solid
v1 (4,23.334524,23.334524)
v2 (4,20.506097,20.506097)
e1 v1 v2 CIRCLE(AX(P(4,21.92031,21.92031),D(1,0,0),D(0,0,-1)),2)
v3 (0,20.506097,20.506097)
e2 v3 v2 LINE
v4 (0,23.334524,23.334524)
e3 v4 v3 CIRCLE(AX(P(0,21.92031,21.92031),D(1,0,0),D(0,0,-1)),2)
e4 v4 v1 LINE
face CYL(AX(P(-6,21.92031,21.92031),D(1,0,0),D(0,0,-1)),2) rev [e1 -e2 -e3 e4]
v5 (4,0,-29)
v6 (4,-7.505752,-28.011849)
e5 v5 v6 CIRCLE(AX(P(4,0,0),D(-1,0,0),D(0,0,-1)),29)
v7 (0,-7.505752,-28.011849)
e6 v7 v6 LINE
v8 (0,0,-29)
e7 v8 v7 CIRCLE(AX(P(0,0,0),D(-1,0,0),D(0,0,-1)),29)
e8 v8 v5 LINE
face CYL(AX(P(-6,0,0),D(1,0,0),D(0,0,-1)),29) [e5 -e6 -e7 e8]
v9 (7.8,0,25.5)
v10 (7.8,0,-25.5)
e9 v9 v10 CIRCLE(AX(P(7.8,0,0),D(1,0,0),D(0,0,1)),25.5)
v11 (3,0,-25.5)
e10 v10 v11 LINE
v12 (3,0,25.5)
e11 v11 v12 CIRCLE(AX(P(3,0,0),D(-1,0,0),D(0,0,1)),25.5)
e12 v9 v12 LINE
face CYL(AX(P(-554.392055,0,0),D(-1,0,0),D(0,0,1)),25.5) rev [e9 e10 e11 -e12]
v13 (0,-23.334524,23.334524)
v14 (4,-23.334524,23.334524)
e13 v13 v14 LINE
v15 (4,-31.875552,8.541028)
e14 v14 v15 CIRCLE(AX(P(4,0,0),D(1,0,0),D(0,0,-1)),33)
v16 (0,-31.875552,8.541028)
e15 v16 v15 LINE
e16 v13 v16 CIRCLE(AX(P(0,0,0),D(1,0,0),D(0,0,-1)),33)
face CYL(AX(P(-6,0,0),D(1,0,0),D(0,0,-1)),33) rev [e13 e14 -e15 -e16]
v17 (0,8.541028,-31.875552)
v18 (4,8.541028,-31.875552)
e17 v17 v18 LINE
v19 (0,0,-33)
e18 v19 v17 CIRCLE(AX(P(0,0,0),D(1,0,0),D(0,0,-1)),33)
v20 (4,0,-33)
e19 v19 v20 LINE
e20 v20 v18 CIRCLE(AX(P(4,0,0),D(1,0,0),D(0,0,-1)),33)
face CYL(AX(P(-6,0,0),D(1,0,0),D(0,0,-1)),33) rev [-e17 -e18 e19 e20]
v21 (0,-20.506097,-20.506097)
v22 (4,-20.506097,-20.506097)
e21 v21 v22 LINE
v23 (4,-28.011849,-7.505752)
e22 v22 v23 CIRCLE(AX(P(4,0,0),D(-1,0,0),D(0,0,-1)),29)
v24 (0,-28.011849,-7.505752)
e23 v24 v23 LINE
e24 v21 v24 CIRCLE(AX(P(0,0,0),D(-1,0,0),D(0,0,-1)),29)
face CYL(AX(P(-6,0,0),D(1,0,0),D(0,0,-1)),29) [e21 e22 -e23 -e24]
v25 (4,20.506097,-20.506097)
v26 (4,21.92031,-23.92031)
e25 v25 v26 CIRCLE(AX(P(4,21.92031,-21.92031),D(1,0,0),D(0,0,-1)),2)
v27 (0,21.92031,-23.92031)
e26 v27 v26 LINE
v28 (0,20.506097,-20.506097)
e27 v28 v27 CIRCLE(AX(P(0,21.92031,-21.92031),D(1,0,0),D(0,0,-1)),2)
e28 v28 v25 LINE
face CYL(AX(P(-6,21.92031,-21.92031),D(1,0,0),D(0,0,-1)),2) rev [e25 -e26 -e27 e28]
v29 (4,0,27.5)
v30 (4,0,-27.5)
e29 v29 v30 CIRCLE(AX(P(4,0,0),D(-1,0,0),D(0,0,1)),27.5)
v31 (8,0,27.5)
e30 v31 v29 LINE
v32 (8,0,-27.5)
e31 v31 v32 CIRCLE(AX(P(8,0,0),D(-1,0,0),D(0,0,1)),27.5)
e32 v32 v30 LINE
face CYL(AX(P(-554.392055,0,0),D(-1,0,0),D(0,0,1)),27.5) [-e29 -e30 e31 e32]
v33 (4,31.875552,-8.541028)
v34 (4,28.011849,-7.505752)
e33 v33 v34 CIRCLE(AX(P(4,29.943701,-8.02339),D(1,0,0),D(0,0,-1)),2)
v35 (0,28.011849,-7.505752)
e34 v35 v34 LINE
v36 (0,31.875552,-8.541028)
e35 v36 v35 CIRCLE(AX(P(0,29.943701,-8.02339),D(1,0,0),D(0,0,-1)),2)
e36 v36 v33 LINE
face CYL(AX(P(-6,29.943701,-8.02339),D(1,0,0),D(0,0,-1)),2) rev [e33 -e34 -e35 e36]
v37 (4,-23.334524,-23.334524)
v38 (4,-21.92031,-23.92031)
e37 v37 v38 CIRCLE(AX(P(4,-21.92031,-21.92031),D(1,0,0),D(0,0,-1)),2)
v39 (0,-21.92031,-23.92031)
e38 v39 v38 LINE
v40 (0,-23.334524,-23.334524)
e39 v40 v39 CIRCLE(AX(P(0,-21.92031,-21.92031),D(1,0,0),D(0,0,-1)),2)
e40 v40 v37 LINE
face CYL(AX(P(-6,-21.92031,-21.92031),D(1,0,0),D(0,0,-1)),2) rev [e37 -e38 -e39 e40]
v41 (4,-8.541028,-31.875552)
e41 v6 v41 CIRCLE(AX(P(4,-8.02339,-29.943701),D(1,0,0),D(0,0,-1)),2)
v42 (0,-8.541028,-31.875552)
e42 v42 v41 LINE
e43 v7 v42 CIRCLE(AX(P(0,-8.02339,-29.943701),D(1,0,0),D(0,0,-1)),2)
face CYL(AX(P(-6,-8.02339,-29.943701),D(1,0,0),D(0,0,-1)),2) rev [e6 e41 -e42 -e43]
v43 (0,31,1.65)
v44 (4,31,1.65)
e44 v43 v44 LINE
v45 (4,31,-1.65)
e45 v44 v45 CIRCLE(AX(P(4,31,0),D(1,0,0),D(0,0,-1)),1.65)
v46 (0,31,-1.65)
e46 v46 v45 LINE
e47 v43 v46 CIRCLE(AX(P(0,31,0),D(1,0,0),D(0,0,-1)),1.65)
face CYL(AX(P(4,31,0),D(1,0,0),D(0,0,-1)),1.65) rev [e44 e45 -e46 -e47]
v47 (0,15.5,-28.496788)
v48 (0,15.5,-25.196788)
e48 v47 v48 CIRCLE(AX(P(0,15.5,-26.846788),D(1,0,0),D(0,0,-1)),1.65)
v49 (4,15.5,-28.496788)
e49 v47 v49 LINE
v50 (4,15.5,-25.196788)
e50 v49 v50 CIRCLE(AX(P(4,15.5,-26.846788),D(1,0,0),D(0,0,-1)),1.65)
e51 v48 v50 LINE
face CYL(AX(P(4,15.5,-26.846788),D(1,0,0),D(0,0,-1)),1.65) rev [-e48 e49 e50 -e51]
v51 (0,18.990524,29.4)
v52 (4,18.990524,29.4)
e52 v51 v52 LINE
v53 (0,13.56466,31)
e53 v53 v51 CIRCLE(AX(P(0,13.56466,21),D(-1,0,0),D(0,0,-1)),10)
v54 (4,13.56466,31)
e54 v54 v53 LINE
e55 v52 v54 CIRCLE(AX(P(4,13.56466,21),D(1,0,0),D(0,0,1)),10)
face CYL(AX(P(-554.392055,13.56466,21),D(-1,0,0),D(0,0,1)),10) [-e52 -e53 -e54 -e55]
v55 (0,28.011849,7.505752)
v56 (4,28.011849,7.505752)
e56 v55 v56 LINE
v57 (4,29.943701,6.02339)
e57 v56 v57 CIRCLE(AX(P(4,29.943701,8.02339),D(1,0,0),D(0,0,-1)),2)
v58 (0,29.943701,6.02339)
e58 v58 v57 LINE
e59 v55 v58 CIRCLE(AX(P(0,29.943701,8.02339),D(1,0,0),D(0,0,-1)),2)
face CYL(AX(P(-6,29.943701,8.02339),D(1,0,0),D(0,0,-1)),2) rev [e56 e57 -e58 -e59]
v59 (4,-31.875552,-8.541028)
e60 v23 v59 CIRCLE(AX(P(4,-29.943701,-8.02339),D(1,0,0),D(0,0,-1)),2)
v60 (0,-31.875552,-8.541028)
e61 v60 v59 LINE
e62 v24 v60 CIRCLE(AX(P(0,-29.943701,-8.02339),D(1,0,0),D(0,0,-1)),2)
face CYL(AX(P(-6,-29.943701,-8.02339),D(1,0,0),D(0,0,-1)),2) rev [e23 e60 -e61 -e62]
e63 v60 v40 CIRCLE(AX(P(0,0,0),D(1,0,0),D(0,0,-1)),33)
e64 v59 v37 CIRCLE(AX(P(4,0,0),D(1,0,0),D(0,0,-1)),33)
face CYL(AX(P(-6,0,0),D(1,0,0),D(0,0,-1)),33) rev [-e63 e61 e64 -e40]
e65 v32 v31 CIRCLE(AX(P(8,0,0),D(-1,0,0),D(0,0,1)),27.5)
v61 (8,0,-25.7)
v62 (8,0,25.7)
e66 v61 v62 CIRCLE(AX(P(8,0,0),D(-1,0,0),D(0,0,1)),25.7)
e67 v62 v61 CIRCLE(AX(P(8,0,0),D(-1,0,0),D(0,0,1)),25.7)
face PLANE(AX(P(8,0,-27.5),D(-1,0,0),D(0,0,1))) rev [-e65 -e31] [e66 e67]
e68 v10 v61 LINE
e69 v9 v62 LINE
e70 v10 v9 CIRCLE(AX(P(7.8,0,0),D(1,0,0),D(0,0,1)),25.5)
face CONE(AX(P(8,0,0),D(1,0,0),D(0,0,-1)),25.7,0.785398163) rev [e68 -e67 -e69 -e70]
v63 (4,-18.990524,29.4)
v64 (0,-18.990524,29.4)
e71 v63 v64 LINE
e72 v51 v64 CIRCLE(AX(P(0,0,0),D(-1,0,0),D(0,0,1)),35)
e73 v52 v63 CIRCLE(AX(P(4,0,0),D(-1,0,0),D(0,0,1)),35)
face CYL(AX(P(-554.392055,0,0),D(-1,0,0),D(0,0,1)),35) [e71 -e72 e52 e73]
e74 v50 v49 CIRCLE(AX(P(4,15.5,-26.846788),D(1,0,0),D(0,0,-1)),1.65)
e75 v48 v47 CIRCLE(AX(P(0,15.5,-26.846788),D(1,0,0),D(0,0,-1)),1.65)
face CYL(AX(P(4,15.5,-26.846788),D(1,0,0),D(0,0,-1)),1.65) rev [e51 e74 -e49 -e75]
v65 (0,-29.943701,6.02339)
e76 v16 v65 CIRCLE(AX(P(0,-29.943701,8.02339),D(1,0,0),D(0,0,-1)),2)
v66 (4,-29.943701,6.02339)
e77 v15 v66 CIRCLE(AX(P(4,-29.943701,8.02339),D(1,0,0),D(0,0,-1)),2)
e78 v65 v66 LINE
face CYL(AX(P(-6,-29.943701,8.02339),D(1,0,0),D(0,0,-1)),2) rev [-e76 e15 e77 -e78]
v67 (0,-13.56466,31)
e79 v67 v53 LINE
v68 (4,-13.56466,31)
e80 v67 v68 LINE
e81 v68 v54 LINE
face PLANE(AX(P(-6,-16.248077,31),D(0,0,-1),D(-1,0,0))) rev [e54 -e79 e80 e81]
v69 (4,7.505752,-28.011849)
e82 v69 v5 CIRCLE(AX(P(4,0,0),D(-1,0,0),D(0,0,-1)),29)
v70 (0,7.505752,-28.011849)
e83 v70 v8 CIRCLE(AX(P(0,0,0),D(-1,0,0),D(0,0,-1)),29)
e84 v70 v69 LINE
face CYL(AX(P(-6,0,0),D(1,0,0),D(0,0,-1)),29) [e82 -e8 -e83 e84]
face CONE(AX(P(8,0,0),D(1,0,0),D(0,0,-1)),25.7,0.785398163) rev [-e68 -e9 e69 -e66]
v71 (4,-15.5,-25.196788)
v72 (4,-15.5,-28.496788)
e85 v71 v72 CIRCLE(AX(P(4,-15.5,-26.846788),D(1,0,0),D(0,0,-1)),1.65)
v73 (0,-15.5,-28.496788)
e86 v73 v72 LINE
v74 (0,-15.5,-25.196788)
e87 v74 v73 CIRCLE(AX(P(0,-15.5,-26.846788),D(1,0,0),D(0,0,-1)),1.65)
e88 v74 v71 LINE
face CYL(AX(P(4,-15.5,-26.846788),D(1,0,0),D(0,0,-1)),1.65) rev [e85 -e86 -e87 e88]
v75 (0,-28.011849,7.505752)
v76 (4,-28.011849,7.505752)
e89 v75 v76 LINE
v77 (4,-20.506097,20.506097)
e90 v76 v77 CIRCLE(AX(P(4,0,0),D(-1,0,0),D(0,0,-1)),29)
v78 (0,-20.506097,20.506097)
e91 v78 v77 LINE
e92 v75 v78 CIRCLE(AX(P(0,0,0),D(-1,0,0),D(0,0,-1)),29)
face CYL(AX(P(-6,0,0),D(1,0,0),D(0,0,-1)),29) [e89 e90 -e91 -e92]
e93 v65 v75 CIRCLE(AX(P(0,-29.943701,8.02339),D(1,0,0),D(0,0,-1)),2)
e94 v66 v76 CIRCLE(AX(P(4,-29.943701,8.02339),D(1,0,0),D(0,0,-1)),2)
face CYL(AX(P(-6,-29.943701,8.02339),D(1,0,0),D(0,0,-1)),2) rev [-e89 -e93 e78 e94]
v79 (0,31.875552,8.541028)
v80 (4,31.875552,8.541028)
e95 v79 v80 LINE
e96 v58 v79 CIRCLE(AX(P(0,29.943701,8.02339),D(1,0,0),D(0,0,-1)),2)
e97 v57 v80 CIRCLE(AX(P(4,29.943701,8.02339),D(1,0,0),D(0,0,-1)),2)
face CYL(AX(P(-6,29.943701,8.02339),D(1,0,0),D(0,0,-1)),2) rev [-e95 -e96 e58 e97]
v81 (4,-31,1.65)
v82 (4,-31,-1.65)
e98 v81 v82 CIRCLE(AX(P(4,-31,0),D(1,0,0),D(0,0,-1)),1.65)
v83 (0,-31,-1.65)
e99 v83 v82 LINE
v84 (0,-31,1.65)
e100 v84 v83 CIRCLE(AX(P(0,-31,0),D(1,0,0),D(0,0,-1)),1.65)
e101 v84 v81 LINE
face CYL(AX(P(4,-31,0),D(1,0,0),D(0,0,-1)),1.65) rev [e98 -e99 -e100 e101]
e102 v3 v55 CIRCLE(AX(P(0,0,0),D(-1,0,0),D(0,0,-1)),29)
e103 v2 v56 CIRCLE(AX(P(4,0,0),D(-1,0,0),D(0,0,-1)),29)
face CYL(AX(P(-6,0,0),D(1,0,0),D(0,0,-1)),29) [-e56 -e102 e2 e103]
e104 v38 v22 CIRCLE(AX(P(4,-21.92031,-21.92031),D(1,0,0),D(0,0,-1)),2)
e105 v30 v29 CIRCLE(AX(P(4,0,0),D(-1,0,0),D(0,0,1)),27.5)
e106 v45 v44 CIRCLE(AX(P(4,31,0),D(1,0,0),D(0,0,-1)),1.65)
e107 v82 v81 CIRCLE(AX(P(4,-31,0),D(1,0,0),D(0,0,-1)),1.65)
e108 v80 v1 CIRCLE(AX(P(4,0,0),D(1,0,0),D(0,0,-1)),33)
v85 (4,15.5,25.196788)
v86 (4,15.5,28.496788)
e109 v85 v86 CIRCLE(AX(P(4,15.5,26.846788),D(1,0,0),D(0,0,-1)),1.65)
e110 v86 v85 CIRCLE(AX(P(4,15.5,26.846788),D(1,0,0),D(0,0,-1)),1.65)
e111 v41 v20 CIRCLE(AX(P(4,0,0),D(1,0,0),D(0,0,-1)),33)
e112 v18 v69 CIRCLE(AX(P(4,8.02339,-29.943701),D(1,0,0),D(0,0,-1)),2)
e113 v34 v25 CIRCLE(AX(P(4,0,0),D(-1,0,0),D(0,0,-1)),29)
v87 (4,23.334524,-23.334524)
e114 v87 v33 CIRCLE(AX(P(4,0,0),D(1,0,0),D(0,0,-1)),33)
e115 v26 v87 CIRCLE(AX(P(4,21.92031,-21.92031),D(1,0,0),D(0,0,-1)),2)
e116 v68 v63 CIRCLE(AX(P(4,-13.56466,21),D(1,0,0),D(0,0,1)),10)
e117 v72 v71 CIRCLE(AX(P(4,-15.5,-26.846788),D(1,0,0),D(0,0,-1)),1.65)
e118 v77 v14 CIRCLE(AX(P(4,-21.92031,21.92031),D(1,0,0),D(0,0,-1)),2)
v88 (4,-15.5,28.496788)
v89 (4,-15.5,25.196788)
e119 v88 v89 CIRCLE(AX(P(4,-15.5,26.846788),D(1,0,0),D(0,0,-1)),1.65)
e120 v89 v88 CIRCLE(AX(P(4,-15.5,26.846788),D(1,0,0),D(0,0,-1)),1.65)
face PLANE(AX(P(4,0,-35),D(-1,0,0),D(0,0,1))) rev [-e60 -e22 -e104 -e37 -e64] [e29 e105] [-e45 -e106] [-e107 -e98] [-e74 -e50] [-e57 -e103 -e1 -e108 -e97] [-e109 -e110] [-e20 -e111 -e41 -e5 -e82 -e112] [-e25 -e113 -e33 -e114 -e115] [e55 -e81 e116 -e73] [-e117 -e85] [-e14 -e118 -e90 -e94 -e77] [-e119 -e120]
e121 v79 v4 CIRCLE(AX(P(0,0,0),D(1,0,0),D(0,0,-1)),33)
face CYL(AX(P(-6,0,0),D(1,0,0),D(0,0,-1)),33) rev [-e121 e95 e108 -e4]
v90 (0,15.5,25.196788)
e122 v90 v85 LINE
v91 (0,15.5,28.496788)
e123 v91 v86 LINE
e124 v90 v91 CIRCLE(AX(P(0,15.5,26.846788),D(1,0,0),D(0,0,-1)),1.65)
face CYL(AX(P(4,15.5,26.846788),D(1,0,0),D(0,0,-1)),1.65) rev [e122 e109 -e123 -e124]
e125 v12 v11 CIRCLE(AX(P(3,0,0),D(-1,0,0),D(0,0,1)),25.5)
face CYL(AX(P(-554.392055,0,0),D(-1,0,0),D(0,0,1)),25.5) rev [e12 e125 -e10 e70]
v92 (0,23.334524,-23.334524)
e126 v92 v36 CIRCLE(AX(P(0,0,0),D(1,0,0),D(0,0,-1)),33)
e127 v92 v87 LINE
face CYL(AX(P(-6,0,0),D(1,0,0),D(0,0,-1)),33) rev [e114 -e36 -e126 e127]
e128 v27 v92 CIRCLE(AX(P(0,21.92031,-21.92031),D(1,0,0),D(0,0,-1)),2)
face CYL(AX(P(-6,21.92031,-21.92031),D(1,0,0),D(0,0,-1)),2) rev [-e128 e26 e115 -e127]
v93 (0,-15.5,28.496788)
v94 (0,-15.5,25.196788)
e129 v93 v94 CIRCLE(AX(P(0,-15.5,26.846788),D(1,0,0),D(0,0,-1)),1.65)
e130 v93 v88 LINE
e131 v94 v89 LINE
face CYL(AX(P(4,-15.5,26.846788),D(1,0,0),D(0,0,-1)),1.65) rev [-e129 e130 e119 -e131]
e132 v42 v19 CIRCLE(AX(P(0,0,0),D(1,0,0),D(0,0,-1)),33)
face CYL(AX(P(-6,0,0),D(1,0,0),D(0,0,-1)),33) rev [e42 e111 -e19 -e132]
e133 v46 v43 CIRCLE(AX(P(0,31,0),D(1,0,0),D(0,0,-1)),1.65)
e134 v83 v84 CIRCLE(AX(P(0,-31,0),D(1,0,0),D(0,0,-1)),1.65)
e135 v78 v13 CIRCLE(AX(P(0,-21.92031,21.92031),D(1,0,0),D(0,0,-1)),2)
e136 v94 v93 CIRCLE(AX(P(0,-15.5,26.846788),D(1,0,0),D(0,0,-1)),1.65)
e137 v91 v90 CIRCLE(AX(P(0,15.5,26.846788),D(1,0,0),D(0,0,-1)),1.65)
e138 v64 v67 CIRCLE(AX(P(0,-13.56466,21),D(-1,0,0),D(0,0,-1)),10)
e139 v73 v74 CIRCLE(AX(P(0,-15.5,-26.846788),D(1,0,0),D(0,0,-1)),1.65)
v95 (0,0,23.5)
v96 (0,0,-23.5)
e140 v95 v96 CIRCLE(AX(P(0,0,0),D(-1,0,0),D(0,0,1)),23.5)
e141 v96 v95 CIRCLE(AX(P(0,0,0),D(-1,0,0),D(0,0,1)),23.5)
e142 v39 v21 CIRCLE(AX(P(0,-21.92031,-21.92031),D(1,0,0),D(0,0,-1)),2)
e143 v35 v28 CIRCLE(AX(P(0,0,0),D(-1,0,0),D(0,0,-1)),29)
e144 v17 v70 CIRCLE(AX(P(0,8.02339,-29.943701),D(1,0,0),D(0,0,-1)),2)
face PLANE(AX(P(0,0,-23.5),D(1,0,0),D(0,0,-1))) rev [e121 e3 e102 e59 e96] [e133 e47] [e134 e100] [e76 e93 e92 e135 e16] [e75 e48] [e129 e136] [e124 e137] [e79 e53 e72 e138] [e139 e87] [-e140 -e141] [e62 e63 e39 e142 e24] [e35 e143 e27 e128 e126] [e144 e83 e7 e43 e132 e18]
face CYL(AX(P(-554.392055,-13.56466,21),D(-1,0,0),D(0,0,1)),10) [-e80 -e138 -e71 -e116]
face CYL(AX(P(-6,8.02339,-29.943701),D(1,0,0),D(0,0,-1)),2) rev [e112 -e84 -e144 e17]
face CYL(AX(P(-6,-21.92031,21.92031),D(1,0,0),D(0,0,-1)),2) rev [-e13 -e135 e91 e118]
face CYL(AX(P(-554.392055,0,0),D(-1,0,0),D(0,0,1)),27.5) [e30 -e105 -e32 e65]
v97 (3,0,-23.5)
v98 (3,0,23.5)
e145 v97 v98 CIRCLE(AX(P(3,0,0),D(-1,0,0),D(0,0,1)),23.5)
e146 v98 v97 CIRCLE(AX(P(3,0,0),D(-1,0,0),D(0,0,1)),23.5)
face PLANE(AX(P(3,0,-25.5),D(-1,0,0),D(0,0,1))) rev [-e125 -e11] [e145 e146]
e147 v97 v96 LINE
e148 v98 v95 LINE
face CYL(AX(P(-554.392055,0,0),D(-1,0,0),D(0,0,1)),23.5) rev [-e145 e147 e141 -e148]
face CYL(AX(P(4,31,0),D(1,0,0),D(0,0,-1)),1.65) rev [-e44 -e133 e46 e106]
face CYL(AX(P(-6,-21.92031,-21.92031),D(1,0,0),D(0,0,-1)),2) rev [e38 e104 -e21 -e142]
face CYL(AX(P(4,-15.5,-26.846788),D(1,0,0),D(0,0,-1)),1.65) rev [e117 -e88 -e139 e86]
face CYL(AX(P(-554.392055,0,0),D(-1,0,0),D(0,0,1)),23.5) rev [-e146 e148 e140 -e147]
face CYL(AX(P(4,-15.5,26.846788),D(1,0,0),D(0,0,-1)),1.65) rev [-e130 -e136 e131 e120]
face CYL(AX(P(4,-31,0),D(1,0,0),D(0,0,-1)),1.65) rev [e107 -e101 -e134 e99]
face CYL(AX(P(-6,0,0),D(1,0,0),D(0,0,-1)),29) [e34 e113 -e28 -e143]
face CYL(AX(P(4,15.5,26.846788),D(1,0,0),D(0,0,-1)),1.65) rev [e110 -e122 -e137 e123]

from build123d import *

# Parameters (mm, degrees)
HOLE_WIZARD_M4_1_D  = 3.3
CUT_EXTRUDE_1_DEPTH = 10
FILLET_1_R          = 10
CUT_EXTRUDE_2_DEPTH = 10
CHAMFER_1_SIZE      = 0.2


with BuildPart() as part:
    # 草图1 → 旋转1 (revolve)
    with BuildSketch(Plane(origin=(0, 0, 0), x_dir=(1, 0, 0), z_dir=(0, 1, 0)), mode=Mode.PRIVATE) as revolve_1_sk:
        Polygon((0, 23.5), (0, 35), (4, 35), (4, 27.5), (8, 27.5), (8, 25.5), (3, 25.5), (3, 23.5), align=None)
    revolve(revolve_1_sk.sketch.rotate(Axis((-554.392054902, 0, 0), (1, 0, 0)), 180), axis=Axis((-554.392054902, 0, 0), (1, 0, 0)))

    # M4 螺纹孔1 (through all)
    with Locations(Plane(origin=(4, 0, 0), x_dir=(0, 0, -1), z_dir=(1, 0, 0))):
        with Locations((0, 0), (0, 31), (26.846787517, 15.5), (26.846787517, -15.5), (0, -31), (-26.846787517, -15.5), (-26.846787517, 15.5)):
            Hole(HOLE_WIZARD_M4_1_D / 2)

    # 草图4 → 切除-拉伸1 (cut)
    with BuildSketch(Plane(origin=(4, 0, 0), x_dir=(0, 0, -1), z_dir=(1, 0, 0))):
        with BuildLine():
            Line((-31, -16.248076809), (-31, 16.248076809))
            ThreePointArc((-31, 16.248076809), (-35, 0), (-31, -16.248076809))
        make_face()
    extrude(amount=-CUT_EXTRUDE_1_DEPTH, mode=Mode.SUBTRACT)

    # 圆角1
    fillet_1_edges = [part.edges().sort_by_distance(p)[0] for p in [
        (2, 16.248076809, 31),
        (2, -16.248076809, 31),
    ]]
    fillet(fillet_1_edges, radius=FILLET_1_R)

    # 草图5 → 切除-拉伸2 (cut)
    with BuildSketch(Plane(origin=(4, 0, 0), x_dir=(0, 0, -1), z_dir=(1, 0, 0))):
        with BuildLine():
            ThreePointArc((23.334523779, 23.334523779), (16.5, 28.578838325), (8.541028488, 31.875552268))
            ThreePointArc((8.541028488, 31.875552268), (6.091538746, 30.461338705), (7.505752308, 28.011848962))
            ThreePointArc((7.505752308, 28.011848962), (14.5, 25.11473671), (20.506096654, 20.506096654))
            ThreePointArc((20.506096654, 20.506096654), (23.334523779, 20.506096654), (23.334523779, 23.334523779))
        make_face()
        with BuildLine():
            ThreePointArc((31.875552268, -8.541028488), (33, 0), (31.875552268, 8.541028488))
            ThreePointArc((31.875552268, 8.541028488), (29.426062525, 9.955242051), (28.011848962, 7.505752308))
            ThreePointArc((28.011848962, 7.505752308), (29, 0), (28.011848962, -7.505752308))
            ThreePointArc((28.011848962, -7.505752308), (29.426062525, -9.955242051), (31.875552268, -8.541028488))
        make_face()
        with BuildLine():
            ThreePointArc((8.541028488, -31.875552268), (16.5, -28.578838325), (23.334523779, -23.334523779))
            ThreePointArc((23.334523779, -23.334523779), (23.334523779, -20.506096654), (20.506096654, -20.506096654))
            ThreePointArc((20.506096654, -20.506096654), (14.5, -25.11473671), (7.505752308, -28.011848962))
            ThreePointArc((7.505752308, -28.011848962), (6.091538746, -30.461338705), (8.541028488, -31.875552268))
        make_face()
        with BuildLine():
            ThreePointArc((-23.334523779, -23.334523779), (-16.5, -28.578838325), (-8.541028488, -31.875552268))
            ThreePointArc((-8.541028488, -31.875552268), (-6.091538746, -30.461338705), (-7.505752308, -28.011848962))
            ThreePointArc((-7.505752308, -28.011848962), (-14.5, -25.11473671), (-20.506096654, -20.506096654))
            ThreePointArc((-20.506096654, -20.506096654), (-23.334523779, -20.506096654), (-23.334523779, -23.334523779))
        make_face()
        with BuildLine():
            ThreePointArc((-8.541028488, 31.875552268), (-16.5, 28.578838325), (-23.334523779, 23.334523779))
            ThreePointArc((-23.334523779, 23.334523779), (-23.334523779, 20.506096654), (-20.506096654, 20.506096654))
            ThreePointArc((-20.506096654, 20.506096654), (-14.5, 25.11473671), (-7.505752308, 28.011848962))
            ThreePointArc((-7.505752308, 28.011848962), (-6.091538746, 30.461338705), (-8.541028488, 31.875552268))
        make_face()
    extrude(amount=-CUT_EXTRUDE_2_DEPTH, mode=Mode.SUBTRACT)

    # 倒角1
    chamfer_1_edges = [part.edges().sort_by_distance(p)[0] for p in [
        (8, 0, -25.5),
    ]]
    chamfer(chamfer_1_edges, length=CHAMFER_1_SIZE)


solid = part.part
